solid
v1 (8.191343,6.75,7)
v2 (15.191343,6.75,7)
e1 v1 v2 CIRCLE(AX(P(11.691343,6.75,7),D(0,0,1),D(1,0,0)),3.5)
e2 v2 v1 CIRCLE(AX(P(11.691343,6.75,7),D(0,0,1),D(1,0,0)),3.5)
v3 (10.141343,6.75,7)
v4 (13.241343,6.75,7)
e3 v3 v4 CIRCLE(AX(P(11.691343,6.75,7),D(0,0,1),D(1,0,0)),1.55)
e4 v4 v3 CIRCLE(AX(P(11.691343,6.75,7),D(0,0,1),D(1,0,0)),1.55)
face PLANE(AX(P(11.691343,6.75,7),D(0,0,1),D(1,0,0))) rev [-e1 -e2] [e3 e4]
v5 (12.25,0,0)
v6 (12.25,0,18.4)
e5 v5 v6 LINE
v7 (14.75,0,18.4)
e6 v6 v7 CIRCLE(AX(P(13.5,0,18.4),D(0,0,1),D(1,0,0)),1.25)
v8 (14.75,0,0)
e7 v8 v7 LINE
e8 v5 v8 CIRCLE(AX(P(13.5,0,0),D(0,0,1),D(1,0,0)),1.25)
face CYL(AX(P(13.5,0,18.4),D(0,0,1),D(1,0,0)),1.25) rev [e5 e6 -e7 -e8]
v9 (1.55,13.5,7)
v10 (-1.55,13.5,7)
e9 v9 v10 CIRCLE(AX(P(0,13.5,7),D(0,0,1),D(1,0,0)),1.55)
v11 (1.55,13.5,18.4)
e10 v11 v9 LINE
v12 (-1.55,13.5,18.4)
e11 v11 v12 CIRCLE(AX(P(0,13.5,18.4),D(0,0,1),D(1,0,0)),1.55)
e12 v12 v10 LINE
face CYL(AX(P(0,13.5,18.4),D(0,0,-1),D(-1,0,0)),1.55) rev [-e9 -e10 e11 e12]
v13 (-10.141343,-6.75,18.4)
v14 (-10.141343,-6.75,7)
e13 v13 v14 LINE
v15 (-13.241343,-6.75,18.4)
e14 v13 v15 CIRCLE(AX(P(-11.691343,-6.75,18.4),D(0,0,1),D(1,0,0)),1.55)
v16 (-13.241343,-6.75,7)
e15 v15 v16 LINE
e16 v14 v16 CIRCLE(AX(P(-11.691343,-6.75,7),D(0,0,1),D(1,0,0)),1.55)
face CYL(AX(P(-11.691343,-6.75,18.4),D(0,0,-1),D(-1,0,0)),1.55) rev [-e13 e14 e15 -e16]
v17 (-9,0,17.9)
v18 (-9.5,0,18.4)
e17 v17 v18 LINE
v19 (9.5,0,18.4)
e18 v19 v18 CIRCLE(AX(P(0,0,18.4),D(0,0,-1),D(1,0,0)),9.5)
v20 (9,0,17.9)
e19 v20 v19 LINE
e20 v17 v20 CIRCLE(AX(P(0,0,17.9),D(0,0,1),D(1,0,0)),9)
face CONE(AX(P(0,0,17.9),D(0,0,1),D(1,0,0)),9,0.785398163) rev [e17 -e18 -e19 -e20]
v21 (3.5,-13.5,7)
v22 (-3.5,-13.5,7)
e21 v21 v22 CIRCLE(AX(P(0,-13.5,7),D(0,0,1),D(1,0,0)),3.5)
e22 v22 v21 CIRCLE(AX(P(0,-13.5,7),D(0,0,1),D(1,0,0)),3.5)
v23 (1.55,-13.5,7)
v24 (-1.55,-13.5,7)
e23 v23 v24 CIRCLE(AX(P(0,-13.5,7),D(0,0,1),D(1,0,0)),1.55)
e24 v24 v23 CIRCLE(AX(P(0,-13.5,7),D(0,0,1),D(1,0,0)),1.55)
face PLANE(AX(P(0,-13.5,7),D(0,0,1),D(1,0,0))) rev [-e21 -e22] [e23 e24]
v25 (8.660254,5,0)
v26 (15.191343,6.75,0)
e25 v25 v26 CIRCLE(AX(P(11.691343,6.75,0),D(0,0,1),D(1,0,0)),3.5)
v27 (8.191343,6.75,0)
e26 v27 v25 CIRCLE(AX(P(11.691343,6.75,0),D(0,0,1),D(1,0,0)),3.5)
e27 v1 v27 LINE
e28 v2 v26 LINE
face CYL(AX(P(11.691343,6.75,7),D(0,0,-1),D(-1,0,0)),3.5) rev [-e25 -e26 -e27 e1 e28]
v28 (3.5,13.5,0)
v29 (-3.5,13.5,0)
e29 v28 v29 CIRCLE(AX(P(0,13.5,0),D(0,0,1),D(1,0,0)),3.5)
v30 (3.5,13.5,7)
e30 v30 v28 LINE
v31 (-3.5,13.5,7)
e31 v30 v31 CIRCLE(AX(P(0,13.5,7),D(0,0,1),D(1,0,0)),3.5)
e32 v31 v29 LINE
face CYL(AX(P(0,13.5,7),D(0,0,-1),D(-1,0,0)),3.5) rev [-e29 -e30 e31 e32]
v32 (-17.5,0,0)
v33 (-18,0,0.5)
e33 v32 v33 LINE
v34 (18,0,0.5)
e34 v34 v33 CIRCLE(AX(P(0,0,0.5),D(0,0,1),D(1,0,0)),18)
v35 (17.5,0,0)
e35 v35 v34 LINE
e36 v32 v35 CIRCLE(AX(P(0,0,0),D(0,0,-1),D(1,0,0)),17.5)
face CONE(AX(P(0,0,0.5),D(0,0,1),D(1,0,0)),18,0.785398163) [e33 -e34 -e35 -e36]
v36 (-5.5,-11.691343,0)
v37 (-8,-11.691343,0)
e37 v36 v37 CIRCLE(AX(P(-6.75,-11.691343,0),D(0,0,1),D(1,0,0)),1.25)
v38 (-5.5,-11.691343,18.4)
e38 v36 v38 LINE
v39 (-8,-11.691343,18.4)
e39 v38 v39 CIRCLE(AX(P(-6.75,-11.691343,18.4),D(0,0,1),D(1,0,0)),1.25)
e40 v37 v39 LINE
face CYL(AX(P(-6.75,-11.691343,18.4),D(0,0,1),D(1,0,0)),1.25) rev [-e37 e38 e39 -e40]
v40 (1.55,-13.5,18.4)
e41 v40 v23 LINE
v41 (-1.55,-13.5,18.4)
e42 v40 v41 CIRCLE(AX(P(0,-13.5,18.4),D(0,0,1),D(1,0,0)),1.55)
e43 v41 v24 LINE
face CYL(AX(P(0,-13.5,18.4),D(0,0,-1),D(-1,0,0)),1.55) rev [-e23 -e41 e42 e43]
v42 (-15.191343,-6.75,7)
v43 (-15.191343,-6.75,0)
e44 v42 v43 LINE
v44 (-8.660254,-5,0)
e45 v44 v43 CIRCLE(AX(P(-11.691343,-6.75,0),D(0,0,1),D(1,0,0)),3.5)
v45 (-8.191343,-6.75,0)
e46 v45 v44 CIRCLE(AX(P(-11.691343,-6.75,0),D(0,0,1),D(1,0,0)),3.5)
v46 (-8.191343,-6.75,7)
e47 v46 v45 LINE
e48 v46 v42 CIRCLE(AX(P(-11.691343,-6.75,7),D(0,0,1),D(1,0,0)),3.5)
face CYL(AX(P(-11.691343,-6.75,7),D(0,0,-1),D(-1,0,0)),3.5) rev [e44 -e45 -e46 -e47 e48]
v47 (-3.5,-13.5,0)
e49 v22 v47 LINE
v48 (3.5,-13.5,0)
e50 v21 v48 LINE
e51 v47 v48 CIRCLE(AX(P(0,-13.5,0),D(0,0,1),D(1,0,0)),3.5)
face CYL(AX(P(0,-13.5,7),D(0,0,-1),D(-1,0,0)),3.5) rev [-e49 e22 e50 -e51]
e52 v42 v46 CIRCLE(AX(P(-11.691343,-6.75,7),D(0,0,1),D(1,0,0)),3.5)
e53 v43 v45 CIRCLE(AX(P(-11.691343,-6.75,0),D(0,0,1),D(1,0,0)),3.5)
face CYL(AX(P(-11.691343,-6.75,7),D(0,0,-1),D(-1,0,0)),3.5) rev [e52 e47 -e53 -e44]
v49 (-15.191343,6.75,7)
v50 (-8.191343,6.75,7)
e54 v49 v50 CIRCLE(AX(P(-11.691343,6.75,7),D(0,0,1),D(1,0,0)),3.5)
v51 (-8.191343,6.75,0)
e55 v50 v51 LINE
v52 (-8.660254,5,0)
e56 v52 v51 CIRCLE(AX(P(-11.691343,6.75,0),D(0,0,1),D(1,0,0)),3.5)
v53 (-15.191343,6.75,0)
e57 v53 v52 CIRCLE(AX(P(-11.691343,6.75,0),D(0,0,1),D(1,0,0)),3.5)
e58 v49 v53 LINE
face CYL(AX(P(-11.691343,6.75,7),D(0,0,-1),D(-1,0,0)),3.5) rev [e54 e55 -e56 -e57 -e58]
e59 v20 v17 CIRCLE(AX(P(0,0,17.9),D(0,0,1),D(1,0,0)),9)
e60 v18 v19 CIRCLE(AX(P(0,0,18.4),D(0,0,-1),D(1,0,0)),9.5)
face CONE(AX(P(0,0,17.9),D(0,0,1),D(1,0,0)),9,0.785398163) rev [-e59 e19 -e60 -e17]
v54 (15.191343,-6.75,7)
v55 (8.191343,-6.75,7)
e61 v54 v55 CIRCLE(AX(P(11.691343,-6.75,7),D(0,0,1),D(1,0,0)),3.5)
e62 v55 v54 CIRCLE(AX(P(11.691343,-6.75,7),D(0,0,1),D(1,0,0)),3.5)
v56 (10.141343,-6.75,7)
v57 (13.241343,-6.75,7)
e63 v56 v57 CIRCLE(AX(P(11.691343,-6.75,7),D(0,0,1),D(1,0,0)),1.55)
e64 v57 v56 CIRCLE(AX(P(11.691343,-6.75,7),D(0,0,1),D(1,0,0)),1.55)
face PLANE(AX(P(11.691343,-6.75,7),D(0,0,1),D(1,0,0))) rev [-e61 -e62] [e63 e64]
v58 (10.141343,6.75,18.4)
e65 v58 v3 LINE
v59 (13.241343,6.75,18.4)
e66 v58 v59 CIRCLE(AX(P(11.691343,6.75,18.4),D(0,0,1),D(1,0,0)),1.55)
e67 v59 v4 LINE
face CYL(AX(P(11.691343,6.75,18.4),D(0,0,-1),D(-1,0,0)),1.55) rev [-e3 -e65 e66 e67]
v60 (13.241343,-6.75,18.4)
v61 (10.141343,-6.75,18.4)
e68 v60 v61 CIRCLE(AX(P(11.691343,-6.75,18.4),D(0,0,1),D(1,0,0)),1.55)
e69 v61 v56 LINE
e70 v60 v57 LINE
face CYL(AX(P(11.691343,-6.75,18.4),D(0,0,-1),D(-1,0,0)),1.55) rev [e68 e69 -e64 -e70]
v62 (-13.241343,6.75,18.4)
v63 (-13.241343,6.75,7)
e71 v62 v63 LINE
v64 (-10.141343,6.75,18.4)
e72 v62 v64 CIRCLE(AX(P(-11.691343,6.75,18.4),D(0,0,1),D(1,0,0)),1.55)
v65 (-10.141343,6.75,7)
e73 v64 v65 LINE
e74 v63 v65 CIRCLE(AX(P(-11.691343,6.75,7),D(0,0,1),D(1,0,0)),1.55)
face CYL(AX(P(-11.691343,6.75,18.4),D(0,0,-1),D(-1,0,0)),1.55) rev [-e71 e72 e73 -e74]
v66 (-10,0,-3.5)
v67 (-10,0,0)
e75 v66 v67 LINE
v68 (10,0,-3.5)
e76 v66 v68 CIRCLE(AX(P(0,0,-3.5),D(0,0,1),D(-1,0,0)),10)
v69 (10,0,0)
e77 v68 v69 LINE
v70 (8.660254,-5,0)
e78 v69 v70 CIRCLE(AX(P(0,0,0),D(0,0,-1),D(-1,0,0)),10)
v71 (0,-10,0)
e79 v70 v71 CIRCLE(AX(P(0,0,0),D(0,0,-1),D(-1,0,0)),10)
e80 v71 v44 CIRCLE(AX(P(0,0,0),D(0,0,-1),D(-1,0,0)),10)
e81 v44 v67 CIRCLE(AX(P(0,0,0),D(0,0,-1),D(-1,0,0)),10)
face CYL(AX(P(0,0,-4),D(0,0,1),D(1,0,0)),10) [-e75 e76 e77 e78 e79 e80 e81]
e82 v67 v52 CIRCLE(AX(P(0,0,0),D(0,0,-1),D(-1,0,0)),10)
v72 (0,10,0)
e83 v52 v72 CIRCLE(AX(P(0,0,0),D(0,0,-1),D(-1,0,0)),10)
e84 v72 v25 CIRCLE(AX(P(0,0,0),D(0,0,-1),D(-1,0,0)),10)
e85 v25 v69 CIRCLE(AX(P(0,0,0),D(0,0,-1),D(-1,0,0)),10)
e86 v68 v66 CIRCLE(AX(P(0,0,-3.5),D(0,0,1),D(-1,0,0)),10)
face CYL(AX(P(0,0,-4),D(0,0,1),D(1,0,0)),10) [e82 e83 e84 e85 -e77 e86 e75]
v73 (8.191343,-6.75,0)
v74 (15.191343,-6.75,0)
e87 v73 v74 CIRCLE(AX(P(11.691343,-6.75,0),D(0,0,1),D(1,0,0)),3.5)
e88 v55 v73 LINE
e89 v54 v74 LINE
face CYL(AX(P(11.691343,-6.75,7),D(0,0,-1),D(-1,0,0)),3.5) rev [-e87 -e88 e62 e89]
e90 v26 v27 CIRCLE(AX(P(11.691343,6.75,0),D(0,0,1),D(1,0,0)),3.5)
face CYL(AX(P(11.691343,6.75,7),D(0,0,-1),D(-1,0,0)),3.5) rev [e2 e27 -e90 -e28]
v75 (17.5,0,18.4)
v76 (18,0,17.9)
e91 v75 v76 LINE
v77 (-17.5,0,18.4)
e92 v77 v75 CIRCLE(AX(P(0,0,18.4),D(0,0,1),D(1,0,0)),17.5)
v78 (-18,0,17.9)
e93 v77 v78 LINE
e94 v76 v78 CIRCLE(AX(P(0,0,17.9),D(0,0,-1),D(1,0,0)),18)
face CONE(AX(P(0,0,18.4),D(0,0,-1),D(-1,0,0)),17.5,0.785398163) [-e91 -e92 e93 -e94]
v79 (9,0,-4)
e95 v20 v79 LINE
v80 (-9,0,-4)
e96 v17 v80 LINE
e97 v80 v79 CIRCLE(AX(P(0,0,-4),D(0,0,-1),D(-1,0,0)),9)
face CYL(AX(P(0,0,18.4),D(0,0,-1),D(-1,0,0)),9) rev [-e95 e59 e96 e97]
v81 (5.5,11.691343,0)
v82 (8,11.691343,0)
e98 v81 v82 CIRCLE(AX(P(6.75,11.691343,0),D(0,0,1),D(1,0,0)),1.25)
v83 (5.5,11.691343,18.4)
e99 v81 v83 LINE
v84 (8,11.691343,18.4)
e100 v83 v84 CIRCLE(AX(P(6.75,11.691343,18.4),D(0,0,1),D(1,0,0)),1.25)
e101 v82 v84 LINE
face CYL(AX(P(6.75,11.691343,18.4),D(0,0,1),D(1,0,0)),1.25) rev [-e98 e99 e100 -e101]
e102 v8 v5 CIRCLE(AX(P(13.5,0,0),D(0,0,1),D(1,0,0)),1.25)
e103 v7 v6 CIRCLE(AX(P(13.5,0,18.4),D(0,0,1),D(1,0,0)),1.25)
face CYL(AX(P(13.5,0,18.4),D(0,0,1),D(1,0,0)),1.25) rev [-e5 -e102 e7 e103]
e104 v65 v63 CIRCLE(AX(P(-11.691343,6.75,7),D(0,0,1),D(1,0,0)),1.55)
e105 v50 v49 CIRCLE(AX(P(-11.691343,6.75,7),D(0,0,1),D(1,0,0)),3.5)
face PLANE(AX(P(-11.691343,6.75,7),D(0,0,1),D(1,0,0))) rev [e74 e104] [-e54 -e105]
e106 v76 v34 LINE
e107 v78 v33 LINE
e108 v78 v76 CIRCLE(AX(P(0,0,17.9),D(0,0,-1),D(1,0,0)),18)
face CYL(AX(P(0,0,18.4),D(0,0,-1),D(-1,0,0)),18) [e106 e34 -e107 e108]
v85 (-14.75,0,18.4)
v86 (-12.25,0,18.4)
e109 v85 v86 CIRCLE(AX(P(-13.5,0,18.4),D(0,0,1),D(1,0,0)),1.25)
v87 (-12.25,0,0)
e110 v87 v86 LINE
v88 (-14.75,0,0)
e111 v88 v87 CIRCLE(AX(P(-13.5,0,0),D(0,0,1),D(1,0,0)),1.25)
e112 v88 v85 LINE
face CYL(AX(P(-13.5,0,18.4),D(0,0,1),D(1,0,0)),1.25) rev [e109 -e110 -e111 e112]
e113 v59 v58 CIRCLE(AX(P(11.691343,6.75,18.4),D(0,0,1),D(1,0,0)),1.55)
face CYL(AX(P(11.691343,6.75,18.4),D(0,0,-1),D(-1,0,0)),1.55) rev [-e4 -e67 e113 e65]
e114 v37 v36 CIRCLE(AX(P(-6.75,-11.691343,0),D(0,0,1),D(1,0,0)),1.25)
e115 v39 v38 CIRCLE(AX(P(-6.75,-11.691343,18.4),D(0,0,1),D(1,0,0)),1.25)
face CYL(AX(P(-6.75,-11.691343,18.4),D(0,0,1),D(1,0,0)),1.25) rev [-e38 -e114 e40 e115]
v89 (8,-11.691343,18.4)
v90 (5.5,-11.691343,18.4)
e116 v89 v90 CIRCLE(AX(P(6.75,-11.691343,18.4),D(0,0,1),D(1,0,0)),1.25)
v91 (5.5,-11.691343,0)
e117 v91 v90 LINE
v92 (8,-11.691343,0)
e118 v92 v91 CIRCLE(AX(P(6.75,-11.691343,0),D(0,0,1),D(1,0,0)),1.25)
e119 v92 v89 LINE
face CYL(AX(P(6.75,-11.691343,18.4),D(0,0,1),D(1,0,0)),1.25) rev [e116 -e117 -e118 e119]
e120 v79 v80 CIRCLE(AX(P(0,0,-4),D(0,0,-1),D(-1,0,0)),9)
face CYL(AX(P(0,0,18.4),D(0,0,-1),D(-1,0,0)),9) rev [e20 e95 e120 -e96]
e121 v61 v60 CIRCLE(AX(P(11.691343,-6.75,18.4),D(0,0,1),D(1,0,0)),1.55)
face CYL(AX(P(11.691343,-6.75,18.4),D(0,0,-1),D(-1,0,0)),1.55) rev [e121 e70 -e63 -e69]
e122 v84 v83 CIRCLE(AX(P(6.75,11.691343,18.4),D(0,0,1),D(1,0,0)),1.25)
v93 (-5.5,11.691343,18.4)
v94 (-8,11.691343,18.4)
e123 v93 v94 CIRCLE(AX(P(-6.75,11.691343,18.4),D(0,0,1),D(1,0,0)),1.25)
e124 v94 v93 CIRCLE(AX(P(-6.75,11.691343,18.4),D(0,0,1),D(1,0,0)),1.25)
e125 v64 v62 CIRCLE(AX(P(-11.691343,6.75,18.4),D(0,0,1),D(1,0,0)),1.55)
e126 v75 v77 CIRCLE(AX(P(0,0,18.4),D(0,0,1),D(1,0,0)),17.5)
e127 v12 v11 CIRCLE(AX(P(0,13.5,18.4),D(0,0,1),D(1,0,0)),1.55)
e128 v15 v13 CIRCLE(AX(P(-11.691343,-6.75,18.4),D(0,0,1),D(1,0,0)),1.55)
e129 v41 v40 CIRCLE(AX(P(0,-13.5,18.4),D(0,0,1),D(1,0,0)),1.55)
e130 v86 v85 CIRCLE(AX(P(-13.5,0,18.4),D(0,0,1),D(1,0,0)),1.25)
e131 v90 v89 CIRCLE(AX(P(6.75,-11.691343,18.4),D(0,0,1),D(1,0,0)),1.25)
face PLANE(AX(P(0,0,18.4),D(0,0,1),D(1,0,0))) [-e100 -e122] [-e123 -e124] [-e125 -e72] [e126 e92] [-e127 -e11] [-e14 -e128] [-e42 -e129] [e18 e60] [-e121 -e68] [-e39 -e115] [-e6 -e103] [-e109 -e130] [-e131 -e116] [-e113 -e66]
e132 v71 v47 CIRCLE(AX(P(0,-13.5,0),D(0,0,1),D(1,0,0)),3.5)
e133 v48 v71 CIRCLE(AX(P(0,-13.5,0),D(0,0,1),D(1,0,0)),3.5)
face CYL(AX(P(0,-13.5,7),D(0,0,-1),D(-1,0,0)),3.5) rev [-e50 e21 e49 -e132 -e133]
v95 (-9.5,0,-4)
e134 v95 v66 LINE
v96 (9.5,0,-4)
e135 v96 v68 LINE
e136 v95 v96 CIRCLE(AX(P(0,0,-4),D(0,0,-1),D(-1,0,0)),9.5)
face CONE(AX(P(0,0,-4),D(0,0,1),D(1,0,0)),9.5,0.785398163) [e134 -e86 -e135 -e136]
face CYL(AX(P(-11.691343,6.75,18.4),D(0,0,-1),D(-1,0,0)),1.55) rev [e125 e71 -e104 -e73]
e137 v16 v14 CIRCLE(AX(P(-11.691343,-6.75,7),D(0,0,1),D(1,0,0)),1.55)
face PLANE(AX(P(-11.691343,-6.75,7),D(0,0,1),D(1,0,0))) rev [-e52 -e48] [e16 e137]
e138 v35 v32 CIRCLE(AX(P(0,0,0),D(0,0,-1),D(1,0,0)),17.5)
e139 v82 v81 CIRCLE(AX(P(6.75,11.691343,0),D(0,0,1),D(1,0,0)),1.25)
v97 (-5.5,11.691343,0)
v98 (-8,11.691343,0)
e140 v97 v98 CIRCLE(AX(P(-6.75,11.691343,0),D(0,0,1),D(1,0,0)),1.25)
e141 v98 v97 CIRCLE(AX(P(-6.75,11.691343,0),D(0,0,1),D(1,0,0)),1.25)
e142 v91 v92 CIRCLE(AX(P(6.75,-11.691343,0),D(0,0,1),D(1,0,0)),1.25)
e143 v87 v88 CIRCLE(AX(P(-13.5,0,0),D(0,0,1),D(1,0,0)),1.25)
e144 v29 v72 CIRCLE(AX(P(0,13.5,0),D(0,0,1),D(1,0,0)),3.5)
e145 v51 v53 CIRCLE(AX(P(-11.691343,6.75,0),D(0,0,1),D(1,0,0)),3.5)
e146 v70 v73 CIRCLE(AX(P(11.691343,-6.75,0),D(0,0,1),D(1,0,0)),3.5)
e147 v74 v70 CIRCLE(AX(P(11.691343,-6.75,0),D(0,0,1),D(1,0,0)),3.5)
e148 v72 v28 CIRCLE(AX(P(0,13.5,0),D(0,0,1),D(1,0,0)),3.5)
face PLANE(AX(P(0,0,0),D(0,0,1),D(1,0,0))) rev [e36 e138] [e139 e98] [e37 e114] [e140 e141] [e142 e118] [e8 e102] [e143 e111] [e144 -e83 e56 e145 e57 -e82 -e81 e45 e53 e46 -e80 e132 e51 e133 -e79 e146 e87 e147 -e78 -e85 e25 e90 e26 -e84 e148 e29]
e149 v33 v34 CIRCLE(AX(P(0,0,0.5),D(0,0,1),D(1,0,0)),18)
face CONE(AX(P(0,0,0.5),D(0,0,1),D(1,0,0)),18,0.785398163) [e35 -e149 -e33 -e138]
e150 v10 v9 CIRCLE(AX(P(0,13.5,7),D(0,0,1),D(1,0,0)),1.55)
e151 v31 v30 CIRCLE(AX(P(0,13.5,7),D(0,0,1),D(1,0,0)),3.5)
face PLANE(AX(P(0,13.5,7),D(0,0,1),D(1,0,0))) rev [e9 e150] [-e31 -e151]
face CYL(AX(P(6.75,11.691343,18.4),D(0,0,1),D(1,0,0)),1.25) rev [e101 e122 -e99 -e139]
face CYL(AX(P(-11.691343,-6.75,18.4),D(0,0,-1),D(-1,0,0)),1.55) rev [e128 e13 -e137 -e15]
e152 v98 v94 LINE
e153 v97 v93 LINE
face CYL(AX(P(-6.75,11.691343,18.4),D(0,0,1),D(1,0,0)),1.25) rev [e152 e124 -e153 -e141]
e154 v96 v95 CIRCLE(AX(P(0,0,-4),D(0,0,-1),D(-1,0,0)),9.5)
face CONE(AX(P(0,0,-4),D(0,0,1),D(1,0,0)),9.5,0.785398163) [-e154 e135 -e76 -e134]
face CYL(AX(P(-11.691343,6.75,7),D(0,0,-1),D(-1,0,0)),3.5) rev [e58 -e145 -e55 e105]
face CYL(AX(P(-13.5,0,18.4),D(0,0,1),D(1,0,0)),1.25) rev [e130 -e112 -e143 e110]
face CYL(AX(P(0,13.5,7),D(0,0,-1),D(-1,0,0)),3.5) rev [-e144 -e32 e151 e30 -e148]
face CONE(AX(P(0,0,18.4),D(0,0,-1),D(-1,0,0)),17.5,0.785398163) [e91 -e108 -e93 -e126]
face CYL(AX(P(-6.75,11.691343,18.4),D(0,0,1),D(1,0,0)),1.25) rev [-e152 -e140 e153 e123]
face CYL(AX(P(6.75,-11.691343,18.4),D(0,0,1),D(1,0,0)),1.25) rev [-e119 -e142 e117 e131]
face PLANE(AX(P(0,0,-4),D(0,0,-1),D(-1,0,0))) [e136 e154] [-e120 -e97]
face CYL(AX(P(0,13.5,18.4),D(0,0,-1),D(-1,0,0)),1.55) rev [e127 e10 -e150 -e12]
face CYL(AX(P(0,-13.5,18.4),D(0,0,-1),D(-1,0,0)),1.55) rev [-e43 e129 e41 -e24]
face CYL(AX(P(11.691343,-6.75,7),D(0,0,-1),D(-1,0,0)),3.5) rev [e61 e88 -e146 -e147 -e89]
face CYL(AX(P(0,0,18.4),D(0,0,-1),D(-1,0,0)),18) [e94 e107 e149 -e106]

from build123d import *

# Parameters (mm, degrees)
SKETCH_1_R          = 18
SKETCH_1_R_2        = 1.55
SKETCH_1_R_3        = 9
EXTRUDE_1_DEPTH     = 18.4
SKETCH_4_R          = 3.5
CUT_EXTRUDE_1_DEPTH = 7
EXTRUDE_START       = 4
SKETCH_5_R          = 10
SKETCH_5_R_2        = 9
EXTRUDE_2_DEPTH     = 4
HOLE_WIZARD_M3_1_D  = 2.5
CHAMFER_1_SIZE      = 0.5


with BuildPart() as part:
    # 草图1 → 凸台-拉伸1 (new body)
    with BuildSketch(Plane.XY):
        with Locations(Location((0, 0, 0), (0, 0, 180))):
            Circle(SKETCH_1_R)
        with Locations(Location((0, 13.5, 0), (0, 0, 180))):
            Circle(SKETCH_1_R_2, mode=Mode.SUBTRACT)
        with Locations(Location((11.691342951, 6.75, 0), (0, 0, 180))):
            Circle(SKETCH_1_R_2, mode=Mode.SUBTRACT)
        with Locations(Location((11.691342951, -6.75, 0), (0, 0, 180))):
            Circle(SKETCH_1_R_2, mode=Mode.SUBTRACT)
        with Locations(Location((0, -13.5, 0), (0, 0, 180))):
            Circle(SKETCH_1_R_2, mode=Mode.SUBTRACT)
        with Locations(Location((-11.691342951, -6.75, 0), (0, 0, 180))):
            Circle(SKETCH_1_R_2, mode=Mode.SUBTRACT)
        with Locations(Location((-11.691342951, 6.75, 0), (0, 0, 180))):
            Circle(SKETCH_1_R_2, mode=Mode.SUBTRACT)
        with Locations(Location((0, 0, 0), (0, 0, 180))):
            Circle(SKETCH_1_R_3, mode=Mode.SUBTRACT)
    extrude(amount=EXTRUDE_1_DEPTH)

    # 草图4 → 切除-拉伸1 (cut)
    with BuildSketch(Plane.XY):
        with Locations((0, 13.5)):
            Circle(SKETCH_4_R)
        with Locations((11.691342951, 6.75)):
            Circle(SKETCH_4_R)
        with Locations((11.691342951, -6.75)):
            Circle(SKETCH_4_R)
        with Locations((0, -13.5)):
            Circle(SKETCH_4_R)
        with Locations((-11.691342951, -6.75)):
            Circle(SKETCH_4_R)
        with Locations((-11.691342951, 6.75)):
            Circle(SKETCH_4_R)
    extrude(amount=CUT_EXTRUDE_1_DEPTH, mode=Mode.SUBTRACT)

    # 草图5 → 凸台-拉伸2 (add)
    with BuildSketch(Plane(origin=(0, 0, 0), x_dir=(-1, 0, 0), z_dir=(0, 0, -1)).offset(EXTRUDE_START)):
        with Locations(Location((0, 0, 0), (0, 0, 209.999869527))):
            Circle(SKETCH_5_R)
        Circle(SKETCH_5_R_2, mode=Mode.SUBTRACT)
    extrude(amount=-EXTRUDE_2_DEPTH)

    # M3 螺纹孔1 (through all)
    with Locations(Plane.XY.offset(18.4)):
        with Locations((13.5, 0), (6.75, -11.691342951), (-6.75, -11.691342951), (-13.5, 0), (-6.75, 11.691342951), (6.75, 11.691342951)):
            Hole(HOLE_WIZARD_M3_1_D / 2)

    # 倒角1
    chamfer_1_edges = [part.edges().sort_by_distance(p)[0] for p in [
        (18, 0, 0),
        (9, 0, 18.4),
        (18, 0, 18.4),
        (-8.660265424, 4.999980279, -4),
    ]]
    chamfer(chamfer_1_edges, length=CHAMFER_1_SIZE)


solid = part.part
